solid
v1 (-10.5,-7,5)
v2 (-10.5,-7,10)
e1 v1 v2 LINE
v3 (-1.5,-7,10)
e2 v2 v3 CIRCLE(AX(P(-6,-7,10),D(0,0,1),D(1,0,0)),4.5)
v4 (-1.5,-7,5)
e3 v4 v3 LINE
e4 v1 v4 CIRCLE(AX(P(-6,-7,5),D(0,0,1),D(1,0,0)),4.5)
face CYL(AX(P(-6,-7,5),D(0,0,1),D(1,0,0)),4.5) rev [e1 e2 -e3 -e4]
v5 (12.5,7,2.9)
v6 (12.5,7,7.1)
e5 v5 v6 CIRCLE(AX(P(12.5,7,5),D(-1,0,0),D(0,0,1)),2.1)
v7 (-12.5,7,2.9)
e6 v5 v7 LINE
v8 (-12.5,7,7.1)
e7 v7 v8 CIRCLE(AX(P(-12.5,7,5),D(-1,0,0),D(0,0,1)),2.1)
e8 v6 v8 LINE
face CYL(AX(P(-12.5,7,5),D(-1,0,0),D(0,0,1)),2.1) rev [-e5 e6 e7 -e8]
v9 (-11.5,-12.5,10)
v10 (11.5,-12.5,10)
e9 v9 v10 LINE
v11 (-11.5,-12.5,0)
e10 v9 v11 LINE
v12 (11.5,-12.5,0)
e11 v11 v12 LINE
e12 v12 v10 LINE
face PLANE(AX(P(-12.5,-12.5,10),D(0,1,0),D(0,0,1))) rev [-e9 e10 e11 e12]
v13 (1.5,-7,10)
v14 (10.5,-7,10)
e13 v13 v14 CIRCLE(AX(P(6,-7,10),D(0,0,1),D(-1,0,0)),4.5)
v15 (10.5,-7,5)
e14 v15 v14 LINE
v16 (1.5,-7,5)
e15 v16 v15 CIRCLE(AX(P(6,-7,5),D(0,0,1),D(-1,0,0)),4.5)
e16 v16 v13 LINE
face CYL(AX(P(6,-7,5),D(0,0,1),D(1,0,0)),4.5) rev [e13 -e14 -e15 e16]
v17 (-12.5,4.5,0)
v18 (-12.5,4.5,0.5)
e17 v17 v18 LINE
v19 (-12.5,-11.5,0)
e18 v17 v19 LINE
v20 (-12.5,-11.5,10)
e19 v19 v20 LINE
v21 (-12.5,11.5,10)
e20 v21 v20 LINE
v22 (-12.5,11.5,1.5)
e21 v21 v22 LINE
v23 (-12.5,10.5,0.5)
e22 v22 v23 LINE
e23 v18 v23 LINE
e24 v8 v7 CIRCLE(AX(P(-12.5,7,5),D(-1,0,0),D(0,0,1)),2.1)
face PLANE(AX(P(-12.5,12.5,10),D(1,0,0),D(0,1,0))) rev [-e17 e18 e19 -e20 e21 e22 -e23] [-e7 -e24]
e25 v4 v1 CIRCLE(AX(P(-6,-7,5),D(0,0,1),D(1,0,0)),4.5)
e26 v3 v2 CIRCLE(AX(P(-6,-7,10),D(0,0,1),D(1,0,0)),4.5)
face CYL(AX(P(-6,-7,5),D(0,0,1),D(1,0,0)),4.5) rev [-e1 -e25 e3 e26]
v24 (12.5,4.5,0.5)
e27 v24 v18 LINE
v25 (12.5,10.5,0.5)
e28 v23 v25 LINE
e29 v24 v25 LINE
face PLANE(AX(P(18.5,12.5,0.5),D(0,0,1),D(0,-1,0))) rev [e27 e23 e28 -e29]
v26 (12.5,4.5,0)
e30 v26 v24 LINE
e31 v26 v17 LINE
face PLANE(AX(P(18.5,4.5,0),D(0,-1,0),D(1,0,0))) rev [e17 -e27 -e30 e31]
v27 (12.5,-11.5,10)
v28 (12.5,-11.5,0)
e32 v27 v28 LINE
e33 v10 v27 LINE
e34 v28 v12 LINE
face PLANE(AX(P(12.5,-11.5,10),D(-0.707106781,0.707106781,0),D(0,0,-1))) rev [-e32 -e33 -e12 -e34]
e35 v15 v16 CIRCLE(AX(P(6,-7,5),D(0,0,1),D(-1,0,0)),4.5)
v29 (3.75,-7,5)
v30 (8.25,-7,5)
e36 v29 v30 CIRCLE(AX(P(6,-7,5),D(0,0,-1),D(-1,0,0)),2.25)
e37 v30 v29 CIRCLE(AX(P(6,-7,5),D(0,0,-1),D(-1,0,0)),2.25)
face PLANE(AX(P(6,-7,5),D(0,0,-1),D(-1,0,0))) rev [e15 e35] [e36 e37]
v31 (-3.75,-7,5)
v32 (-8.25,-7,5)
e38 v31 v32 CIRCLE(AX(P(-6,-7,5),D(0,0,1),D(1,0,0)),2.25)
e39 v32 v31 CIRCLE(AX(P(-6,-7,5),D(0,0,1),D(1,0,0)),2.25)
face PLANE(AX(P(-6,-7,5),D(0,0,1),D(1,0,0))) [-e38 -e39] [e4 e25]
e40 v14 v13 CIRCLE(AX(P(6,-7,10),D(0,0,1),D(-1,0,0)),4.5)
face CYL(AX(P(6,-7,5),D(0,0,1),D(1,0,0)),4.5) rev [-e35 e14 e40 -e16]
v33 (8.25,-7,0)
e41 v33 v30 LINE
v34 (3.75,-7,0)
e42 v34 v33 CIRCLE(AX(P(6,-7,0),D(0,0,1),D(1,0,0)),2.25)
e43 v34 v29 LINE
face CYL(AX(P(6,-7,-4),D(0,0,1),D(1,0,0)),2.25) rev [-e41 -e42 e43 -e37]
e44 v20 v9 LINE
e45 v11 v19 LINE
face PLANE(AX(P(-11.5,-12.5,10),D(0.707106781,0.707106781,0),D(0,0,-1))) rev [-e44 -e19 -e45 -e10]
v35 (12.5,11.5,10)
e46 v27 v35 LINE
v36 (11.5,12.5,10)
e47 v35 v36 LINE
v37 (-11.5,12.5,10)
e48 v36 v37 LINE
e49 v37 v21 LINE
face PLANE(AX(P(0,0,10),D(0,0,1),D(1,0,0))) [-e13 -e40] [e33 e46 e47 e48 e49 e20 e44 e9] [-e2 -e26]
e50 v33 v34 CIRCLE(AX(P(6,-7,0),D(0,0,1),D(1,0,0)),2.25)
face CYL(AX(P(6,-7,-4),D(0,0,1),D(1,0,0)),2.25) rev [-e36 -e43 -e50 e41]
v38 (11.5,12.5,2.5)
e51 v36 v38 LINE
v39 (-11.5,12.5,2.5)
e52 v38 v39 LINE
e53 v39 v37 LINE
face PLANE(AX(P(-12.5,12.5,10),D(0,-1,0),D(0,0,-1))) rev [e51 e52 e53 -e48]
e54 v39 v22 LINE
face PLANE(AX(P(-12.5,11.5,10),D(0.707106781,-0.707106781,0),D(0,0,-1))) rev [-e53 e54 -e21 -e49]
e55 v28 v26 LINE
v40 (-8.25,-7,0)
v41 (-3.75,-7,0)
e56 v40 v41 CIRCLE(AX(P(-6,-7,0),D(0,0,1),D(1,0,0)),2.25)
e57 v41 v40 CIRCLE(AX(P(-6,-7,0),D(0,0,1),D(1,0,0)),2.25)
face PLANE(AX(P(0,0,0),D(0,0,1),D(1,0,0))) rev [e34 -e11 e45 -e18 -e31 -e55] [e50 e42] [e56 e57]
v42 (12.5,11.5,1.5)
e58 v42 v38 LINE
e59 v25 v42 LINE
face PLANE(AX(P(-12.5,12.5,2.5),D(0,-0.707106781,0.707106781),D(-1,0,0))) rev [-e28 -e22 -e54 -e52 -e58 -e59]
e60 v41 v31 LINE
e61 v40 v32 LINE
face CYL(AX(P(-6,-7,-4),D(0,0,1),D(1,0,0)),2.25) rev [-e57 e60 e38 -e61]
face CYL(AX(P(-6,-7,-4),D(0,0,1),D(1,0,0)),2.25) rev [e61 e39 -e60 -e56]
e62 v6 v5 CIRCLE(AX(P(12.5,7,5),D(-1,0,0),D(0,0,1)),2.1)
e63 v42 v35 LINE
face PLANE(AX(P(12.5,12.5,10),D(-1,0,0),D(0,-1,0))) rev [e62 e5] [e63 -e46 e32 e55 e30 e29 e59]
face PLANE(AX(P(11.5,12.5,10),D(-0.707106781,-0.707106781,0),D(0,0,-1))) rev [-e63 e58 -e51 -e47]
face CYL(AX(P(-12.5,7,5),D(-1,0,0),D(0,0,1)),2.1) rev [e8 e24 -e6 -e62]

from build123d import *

# Parameters (mm, degrees)
SKETCH1_W           = 25
SKETCH1_H           = 25
BOSS_EXTRUDE1_DEPTH = 10
SKETCH3_R           = 4.5
CUT_EXTRUDE2_DEPTH  = 5
SKETCH4_R           = 2.25
CUT_EXTRUDE3_DEPTH  = 14
SKETCH5_R           = 0.905939467
CUT_EXTRUDE4_DEPTH  = 31
M5_TAPPED_HOLE1_D   = 4.2
CHAMFER1_SIZE       = 1
SKETCH8_W           = 0.5
SKETCH8_H           = 8
CUT_EXTRUDE5_DEPTH  = 31
CHAMFER2_SIZE       = 2


with BuildPart() as part:
    # Sketch1 → Boss-Extrude1 (new body)
    with BuildSketch(Plane.XY):
        Rectangle(SKETCH1_W, SKETCH1_H)
    extrude(amount=BOSS_EXTRUDE1_DEPTH)

    # Sketch3 → Cut-Extrude2 (cut)
    with BuildSketch(Plane.XY.offset(10)):
        with Locations((-6, -7)):
            Circle(SKETCH3_R)
        with Locations(Location((6, -7, 0), (0, 0, 180))):
            Circle(SKETCH3_R)
    extrude(amount=-CUT_EXTRUDE2_DEPTH, mode=Mode.SUBTRACT)

    # Sketch4 → Cut-Extrude3 (cut)
    with BuildSketch(Plane.XY.offset(10)):
        with Locations((-6, -7)):
            Circle(SKETCH4_R)
        with Locations((6, -7)):
            Circle(SKETCH4_R)
    extrude(amount=-CUT_EXTRUDE3_DEPTH, mode=Mode.SUBTRACT)

    # Sketch5 → Cut-Extrude4 (cut)
    with BuildSketch(Plane.ZY.offset(12.5)):
        with Locations(Location((5, 7, 0), (0, 0, 270))):
            Circle(SKETCH5_R)
    extrude(amount=-CUT_EXTRUDE4_DEPTH, mode=Mode.SUBTRACT)

    # M5 Tapped Hole1 (through all)
    with Locations(Plane(origin=(-12.5, 7, 5), x_dir=(0, -1, 0), z_dir=(-1, 0, 0))):
        with Locations((0, 0)):
            Hole(M5_TAPPED_HOLE1_D / 2)

    # Chamfer1
    chamfer1_edges = [part.edges().sort_by_distance(p)[0] for p in [
        (12.5, -12.5, 5),
        (-12.5, -12.5, 5),
        (-12.5, 12.5, 5),
        (12.5, 12.5, 5),
    ]]
    chamfer(chamfer1_edges, length=CHAMFER1_SIZE)

    # Sketch8 → Cut-Extrude5 (cut)
    with BuildSketch(Plane.ZY.offset(12.5)):
        with Locations((0.25, 8.5)):
            Rectangle(SKETCH8_W, SKETCH8_H)
    extrude(amount=-CUT_EXTRUDE5_DEPTH, mode=Mode.SUBTRACT)

    # Chamfer2
    chamfer2_edges = [part.edges().sort_by_distance(p)[0] for p in [
        (0, 12.5, 0.5),
    ]]
    chamfer(chamfer2_edges, length=CHAMFER2_SIZE)


solid = part.part
